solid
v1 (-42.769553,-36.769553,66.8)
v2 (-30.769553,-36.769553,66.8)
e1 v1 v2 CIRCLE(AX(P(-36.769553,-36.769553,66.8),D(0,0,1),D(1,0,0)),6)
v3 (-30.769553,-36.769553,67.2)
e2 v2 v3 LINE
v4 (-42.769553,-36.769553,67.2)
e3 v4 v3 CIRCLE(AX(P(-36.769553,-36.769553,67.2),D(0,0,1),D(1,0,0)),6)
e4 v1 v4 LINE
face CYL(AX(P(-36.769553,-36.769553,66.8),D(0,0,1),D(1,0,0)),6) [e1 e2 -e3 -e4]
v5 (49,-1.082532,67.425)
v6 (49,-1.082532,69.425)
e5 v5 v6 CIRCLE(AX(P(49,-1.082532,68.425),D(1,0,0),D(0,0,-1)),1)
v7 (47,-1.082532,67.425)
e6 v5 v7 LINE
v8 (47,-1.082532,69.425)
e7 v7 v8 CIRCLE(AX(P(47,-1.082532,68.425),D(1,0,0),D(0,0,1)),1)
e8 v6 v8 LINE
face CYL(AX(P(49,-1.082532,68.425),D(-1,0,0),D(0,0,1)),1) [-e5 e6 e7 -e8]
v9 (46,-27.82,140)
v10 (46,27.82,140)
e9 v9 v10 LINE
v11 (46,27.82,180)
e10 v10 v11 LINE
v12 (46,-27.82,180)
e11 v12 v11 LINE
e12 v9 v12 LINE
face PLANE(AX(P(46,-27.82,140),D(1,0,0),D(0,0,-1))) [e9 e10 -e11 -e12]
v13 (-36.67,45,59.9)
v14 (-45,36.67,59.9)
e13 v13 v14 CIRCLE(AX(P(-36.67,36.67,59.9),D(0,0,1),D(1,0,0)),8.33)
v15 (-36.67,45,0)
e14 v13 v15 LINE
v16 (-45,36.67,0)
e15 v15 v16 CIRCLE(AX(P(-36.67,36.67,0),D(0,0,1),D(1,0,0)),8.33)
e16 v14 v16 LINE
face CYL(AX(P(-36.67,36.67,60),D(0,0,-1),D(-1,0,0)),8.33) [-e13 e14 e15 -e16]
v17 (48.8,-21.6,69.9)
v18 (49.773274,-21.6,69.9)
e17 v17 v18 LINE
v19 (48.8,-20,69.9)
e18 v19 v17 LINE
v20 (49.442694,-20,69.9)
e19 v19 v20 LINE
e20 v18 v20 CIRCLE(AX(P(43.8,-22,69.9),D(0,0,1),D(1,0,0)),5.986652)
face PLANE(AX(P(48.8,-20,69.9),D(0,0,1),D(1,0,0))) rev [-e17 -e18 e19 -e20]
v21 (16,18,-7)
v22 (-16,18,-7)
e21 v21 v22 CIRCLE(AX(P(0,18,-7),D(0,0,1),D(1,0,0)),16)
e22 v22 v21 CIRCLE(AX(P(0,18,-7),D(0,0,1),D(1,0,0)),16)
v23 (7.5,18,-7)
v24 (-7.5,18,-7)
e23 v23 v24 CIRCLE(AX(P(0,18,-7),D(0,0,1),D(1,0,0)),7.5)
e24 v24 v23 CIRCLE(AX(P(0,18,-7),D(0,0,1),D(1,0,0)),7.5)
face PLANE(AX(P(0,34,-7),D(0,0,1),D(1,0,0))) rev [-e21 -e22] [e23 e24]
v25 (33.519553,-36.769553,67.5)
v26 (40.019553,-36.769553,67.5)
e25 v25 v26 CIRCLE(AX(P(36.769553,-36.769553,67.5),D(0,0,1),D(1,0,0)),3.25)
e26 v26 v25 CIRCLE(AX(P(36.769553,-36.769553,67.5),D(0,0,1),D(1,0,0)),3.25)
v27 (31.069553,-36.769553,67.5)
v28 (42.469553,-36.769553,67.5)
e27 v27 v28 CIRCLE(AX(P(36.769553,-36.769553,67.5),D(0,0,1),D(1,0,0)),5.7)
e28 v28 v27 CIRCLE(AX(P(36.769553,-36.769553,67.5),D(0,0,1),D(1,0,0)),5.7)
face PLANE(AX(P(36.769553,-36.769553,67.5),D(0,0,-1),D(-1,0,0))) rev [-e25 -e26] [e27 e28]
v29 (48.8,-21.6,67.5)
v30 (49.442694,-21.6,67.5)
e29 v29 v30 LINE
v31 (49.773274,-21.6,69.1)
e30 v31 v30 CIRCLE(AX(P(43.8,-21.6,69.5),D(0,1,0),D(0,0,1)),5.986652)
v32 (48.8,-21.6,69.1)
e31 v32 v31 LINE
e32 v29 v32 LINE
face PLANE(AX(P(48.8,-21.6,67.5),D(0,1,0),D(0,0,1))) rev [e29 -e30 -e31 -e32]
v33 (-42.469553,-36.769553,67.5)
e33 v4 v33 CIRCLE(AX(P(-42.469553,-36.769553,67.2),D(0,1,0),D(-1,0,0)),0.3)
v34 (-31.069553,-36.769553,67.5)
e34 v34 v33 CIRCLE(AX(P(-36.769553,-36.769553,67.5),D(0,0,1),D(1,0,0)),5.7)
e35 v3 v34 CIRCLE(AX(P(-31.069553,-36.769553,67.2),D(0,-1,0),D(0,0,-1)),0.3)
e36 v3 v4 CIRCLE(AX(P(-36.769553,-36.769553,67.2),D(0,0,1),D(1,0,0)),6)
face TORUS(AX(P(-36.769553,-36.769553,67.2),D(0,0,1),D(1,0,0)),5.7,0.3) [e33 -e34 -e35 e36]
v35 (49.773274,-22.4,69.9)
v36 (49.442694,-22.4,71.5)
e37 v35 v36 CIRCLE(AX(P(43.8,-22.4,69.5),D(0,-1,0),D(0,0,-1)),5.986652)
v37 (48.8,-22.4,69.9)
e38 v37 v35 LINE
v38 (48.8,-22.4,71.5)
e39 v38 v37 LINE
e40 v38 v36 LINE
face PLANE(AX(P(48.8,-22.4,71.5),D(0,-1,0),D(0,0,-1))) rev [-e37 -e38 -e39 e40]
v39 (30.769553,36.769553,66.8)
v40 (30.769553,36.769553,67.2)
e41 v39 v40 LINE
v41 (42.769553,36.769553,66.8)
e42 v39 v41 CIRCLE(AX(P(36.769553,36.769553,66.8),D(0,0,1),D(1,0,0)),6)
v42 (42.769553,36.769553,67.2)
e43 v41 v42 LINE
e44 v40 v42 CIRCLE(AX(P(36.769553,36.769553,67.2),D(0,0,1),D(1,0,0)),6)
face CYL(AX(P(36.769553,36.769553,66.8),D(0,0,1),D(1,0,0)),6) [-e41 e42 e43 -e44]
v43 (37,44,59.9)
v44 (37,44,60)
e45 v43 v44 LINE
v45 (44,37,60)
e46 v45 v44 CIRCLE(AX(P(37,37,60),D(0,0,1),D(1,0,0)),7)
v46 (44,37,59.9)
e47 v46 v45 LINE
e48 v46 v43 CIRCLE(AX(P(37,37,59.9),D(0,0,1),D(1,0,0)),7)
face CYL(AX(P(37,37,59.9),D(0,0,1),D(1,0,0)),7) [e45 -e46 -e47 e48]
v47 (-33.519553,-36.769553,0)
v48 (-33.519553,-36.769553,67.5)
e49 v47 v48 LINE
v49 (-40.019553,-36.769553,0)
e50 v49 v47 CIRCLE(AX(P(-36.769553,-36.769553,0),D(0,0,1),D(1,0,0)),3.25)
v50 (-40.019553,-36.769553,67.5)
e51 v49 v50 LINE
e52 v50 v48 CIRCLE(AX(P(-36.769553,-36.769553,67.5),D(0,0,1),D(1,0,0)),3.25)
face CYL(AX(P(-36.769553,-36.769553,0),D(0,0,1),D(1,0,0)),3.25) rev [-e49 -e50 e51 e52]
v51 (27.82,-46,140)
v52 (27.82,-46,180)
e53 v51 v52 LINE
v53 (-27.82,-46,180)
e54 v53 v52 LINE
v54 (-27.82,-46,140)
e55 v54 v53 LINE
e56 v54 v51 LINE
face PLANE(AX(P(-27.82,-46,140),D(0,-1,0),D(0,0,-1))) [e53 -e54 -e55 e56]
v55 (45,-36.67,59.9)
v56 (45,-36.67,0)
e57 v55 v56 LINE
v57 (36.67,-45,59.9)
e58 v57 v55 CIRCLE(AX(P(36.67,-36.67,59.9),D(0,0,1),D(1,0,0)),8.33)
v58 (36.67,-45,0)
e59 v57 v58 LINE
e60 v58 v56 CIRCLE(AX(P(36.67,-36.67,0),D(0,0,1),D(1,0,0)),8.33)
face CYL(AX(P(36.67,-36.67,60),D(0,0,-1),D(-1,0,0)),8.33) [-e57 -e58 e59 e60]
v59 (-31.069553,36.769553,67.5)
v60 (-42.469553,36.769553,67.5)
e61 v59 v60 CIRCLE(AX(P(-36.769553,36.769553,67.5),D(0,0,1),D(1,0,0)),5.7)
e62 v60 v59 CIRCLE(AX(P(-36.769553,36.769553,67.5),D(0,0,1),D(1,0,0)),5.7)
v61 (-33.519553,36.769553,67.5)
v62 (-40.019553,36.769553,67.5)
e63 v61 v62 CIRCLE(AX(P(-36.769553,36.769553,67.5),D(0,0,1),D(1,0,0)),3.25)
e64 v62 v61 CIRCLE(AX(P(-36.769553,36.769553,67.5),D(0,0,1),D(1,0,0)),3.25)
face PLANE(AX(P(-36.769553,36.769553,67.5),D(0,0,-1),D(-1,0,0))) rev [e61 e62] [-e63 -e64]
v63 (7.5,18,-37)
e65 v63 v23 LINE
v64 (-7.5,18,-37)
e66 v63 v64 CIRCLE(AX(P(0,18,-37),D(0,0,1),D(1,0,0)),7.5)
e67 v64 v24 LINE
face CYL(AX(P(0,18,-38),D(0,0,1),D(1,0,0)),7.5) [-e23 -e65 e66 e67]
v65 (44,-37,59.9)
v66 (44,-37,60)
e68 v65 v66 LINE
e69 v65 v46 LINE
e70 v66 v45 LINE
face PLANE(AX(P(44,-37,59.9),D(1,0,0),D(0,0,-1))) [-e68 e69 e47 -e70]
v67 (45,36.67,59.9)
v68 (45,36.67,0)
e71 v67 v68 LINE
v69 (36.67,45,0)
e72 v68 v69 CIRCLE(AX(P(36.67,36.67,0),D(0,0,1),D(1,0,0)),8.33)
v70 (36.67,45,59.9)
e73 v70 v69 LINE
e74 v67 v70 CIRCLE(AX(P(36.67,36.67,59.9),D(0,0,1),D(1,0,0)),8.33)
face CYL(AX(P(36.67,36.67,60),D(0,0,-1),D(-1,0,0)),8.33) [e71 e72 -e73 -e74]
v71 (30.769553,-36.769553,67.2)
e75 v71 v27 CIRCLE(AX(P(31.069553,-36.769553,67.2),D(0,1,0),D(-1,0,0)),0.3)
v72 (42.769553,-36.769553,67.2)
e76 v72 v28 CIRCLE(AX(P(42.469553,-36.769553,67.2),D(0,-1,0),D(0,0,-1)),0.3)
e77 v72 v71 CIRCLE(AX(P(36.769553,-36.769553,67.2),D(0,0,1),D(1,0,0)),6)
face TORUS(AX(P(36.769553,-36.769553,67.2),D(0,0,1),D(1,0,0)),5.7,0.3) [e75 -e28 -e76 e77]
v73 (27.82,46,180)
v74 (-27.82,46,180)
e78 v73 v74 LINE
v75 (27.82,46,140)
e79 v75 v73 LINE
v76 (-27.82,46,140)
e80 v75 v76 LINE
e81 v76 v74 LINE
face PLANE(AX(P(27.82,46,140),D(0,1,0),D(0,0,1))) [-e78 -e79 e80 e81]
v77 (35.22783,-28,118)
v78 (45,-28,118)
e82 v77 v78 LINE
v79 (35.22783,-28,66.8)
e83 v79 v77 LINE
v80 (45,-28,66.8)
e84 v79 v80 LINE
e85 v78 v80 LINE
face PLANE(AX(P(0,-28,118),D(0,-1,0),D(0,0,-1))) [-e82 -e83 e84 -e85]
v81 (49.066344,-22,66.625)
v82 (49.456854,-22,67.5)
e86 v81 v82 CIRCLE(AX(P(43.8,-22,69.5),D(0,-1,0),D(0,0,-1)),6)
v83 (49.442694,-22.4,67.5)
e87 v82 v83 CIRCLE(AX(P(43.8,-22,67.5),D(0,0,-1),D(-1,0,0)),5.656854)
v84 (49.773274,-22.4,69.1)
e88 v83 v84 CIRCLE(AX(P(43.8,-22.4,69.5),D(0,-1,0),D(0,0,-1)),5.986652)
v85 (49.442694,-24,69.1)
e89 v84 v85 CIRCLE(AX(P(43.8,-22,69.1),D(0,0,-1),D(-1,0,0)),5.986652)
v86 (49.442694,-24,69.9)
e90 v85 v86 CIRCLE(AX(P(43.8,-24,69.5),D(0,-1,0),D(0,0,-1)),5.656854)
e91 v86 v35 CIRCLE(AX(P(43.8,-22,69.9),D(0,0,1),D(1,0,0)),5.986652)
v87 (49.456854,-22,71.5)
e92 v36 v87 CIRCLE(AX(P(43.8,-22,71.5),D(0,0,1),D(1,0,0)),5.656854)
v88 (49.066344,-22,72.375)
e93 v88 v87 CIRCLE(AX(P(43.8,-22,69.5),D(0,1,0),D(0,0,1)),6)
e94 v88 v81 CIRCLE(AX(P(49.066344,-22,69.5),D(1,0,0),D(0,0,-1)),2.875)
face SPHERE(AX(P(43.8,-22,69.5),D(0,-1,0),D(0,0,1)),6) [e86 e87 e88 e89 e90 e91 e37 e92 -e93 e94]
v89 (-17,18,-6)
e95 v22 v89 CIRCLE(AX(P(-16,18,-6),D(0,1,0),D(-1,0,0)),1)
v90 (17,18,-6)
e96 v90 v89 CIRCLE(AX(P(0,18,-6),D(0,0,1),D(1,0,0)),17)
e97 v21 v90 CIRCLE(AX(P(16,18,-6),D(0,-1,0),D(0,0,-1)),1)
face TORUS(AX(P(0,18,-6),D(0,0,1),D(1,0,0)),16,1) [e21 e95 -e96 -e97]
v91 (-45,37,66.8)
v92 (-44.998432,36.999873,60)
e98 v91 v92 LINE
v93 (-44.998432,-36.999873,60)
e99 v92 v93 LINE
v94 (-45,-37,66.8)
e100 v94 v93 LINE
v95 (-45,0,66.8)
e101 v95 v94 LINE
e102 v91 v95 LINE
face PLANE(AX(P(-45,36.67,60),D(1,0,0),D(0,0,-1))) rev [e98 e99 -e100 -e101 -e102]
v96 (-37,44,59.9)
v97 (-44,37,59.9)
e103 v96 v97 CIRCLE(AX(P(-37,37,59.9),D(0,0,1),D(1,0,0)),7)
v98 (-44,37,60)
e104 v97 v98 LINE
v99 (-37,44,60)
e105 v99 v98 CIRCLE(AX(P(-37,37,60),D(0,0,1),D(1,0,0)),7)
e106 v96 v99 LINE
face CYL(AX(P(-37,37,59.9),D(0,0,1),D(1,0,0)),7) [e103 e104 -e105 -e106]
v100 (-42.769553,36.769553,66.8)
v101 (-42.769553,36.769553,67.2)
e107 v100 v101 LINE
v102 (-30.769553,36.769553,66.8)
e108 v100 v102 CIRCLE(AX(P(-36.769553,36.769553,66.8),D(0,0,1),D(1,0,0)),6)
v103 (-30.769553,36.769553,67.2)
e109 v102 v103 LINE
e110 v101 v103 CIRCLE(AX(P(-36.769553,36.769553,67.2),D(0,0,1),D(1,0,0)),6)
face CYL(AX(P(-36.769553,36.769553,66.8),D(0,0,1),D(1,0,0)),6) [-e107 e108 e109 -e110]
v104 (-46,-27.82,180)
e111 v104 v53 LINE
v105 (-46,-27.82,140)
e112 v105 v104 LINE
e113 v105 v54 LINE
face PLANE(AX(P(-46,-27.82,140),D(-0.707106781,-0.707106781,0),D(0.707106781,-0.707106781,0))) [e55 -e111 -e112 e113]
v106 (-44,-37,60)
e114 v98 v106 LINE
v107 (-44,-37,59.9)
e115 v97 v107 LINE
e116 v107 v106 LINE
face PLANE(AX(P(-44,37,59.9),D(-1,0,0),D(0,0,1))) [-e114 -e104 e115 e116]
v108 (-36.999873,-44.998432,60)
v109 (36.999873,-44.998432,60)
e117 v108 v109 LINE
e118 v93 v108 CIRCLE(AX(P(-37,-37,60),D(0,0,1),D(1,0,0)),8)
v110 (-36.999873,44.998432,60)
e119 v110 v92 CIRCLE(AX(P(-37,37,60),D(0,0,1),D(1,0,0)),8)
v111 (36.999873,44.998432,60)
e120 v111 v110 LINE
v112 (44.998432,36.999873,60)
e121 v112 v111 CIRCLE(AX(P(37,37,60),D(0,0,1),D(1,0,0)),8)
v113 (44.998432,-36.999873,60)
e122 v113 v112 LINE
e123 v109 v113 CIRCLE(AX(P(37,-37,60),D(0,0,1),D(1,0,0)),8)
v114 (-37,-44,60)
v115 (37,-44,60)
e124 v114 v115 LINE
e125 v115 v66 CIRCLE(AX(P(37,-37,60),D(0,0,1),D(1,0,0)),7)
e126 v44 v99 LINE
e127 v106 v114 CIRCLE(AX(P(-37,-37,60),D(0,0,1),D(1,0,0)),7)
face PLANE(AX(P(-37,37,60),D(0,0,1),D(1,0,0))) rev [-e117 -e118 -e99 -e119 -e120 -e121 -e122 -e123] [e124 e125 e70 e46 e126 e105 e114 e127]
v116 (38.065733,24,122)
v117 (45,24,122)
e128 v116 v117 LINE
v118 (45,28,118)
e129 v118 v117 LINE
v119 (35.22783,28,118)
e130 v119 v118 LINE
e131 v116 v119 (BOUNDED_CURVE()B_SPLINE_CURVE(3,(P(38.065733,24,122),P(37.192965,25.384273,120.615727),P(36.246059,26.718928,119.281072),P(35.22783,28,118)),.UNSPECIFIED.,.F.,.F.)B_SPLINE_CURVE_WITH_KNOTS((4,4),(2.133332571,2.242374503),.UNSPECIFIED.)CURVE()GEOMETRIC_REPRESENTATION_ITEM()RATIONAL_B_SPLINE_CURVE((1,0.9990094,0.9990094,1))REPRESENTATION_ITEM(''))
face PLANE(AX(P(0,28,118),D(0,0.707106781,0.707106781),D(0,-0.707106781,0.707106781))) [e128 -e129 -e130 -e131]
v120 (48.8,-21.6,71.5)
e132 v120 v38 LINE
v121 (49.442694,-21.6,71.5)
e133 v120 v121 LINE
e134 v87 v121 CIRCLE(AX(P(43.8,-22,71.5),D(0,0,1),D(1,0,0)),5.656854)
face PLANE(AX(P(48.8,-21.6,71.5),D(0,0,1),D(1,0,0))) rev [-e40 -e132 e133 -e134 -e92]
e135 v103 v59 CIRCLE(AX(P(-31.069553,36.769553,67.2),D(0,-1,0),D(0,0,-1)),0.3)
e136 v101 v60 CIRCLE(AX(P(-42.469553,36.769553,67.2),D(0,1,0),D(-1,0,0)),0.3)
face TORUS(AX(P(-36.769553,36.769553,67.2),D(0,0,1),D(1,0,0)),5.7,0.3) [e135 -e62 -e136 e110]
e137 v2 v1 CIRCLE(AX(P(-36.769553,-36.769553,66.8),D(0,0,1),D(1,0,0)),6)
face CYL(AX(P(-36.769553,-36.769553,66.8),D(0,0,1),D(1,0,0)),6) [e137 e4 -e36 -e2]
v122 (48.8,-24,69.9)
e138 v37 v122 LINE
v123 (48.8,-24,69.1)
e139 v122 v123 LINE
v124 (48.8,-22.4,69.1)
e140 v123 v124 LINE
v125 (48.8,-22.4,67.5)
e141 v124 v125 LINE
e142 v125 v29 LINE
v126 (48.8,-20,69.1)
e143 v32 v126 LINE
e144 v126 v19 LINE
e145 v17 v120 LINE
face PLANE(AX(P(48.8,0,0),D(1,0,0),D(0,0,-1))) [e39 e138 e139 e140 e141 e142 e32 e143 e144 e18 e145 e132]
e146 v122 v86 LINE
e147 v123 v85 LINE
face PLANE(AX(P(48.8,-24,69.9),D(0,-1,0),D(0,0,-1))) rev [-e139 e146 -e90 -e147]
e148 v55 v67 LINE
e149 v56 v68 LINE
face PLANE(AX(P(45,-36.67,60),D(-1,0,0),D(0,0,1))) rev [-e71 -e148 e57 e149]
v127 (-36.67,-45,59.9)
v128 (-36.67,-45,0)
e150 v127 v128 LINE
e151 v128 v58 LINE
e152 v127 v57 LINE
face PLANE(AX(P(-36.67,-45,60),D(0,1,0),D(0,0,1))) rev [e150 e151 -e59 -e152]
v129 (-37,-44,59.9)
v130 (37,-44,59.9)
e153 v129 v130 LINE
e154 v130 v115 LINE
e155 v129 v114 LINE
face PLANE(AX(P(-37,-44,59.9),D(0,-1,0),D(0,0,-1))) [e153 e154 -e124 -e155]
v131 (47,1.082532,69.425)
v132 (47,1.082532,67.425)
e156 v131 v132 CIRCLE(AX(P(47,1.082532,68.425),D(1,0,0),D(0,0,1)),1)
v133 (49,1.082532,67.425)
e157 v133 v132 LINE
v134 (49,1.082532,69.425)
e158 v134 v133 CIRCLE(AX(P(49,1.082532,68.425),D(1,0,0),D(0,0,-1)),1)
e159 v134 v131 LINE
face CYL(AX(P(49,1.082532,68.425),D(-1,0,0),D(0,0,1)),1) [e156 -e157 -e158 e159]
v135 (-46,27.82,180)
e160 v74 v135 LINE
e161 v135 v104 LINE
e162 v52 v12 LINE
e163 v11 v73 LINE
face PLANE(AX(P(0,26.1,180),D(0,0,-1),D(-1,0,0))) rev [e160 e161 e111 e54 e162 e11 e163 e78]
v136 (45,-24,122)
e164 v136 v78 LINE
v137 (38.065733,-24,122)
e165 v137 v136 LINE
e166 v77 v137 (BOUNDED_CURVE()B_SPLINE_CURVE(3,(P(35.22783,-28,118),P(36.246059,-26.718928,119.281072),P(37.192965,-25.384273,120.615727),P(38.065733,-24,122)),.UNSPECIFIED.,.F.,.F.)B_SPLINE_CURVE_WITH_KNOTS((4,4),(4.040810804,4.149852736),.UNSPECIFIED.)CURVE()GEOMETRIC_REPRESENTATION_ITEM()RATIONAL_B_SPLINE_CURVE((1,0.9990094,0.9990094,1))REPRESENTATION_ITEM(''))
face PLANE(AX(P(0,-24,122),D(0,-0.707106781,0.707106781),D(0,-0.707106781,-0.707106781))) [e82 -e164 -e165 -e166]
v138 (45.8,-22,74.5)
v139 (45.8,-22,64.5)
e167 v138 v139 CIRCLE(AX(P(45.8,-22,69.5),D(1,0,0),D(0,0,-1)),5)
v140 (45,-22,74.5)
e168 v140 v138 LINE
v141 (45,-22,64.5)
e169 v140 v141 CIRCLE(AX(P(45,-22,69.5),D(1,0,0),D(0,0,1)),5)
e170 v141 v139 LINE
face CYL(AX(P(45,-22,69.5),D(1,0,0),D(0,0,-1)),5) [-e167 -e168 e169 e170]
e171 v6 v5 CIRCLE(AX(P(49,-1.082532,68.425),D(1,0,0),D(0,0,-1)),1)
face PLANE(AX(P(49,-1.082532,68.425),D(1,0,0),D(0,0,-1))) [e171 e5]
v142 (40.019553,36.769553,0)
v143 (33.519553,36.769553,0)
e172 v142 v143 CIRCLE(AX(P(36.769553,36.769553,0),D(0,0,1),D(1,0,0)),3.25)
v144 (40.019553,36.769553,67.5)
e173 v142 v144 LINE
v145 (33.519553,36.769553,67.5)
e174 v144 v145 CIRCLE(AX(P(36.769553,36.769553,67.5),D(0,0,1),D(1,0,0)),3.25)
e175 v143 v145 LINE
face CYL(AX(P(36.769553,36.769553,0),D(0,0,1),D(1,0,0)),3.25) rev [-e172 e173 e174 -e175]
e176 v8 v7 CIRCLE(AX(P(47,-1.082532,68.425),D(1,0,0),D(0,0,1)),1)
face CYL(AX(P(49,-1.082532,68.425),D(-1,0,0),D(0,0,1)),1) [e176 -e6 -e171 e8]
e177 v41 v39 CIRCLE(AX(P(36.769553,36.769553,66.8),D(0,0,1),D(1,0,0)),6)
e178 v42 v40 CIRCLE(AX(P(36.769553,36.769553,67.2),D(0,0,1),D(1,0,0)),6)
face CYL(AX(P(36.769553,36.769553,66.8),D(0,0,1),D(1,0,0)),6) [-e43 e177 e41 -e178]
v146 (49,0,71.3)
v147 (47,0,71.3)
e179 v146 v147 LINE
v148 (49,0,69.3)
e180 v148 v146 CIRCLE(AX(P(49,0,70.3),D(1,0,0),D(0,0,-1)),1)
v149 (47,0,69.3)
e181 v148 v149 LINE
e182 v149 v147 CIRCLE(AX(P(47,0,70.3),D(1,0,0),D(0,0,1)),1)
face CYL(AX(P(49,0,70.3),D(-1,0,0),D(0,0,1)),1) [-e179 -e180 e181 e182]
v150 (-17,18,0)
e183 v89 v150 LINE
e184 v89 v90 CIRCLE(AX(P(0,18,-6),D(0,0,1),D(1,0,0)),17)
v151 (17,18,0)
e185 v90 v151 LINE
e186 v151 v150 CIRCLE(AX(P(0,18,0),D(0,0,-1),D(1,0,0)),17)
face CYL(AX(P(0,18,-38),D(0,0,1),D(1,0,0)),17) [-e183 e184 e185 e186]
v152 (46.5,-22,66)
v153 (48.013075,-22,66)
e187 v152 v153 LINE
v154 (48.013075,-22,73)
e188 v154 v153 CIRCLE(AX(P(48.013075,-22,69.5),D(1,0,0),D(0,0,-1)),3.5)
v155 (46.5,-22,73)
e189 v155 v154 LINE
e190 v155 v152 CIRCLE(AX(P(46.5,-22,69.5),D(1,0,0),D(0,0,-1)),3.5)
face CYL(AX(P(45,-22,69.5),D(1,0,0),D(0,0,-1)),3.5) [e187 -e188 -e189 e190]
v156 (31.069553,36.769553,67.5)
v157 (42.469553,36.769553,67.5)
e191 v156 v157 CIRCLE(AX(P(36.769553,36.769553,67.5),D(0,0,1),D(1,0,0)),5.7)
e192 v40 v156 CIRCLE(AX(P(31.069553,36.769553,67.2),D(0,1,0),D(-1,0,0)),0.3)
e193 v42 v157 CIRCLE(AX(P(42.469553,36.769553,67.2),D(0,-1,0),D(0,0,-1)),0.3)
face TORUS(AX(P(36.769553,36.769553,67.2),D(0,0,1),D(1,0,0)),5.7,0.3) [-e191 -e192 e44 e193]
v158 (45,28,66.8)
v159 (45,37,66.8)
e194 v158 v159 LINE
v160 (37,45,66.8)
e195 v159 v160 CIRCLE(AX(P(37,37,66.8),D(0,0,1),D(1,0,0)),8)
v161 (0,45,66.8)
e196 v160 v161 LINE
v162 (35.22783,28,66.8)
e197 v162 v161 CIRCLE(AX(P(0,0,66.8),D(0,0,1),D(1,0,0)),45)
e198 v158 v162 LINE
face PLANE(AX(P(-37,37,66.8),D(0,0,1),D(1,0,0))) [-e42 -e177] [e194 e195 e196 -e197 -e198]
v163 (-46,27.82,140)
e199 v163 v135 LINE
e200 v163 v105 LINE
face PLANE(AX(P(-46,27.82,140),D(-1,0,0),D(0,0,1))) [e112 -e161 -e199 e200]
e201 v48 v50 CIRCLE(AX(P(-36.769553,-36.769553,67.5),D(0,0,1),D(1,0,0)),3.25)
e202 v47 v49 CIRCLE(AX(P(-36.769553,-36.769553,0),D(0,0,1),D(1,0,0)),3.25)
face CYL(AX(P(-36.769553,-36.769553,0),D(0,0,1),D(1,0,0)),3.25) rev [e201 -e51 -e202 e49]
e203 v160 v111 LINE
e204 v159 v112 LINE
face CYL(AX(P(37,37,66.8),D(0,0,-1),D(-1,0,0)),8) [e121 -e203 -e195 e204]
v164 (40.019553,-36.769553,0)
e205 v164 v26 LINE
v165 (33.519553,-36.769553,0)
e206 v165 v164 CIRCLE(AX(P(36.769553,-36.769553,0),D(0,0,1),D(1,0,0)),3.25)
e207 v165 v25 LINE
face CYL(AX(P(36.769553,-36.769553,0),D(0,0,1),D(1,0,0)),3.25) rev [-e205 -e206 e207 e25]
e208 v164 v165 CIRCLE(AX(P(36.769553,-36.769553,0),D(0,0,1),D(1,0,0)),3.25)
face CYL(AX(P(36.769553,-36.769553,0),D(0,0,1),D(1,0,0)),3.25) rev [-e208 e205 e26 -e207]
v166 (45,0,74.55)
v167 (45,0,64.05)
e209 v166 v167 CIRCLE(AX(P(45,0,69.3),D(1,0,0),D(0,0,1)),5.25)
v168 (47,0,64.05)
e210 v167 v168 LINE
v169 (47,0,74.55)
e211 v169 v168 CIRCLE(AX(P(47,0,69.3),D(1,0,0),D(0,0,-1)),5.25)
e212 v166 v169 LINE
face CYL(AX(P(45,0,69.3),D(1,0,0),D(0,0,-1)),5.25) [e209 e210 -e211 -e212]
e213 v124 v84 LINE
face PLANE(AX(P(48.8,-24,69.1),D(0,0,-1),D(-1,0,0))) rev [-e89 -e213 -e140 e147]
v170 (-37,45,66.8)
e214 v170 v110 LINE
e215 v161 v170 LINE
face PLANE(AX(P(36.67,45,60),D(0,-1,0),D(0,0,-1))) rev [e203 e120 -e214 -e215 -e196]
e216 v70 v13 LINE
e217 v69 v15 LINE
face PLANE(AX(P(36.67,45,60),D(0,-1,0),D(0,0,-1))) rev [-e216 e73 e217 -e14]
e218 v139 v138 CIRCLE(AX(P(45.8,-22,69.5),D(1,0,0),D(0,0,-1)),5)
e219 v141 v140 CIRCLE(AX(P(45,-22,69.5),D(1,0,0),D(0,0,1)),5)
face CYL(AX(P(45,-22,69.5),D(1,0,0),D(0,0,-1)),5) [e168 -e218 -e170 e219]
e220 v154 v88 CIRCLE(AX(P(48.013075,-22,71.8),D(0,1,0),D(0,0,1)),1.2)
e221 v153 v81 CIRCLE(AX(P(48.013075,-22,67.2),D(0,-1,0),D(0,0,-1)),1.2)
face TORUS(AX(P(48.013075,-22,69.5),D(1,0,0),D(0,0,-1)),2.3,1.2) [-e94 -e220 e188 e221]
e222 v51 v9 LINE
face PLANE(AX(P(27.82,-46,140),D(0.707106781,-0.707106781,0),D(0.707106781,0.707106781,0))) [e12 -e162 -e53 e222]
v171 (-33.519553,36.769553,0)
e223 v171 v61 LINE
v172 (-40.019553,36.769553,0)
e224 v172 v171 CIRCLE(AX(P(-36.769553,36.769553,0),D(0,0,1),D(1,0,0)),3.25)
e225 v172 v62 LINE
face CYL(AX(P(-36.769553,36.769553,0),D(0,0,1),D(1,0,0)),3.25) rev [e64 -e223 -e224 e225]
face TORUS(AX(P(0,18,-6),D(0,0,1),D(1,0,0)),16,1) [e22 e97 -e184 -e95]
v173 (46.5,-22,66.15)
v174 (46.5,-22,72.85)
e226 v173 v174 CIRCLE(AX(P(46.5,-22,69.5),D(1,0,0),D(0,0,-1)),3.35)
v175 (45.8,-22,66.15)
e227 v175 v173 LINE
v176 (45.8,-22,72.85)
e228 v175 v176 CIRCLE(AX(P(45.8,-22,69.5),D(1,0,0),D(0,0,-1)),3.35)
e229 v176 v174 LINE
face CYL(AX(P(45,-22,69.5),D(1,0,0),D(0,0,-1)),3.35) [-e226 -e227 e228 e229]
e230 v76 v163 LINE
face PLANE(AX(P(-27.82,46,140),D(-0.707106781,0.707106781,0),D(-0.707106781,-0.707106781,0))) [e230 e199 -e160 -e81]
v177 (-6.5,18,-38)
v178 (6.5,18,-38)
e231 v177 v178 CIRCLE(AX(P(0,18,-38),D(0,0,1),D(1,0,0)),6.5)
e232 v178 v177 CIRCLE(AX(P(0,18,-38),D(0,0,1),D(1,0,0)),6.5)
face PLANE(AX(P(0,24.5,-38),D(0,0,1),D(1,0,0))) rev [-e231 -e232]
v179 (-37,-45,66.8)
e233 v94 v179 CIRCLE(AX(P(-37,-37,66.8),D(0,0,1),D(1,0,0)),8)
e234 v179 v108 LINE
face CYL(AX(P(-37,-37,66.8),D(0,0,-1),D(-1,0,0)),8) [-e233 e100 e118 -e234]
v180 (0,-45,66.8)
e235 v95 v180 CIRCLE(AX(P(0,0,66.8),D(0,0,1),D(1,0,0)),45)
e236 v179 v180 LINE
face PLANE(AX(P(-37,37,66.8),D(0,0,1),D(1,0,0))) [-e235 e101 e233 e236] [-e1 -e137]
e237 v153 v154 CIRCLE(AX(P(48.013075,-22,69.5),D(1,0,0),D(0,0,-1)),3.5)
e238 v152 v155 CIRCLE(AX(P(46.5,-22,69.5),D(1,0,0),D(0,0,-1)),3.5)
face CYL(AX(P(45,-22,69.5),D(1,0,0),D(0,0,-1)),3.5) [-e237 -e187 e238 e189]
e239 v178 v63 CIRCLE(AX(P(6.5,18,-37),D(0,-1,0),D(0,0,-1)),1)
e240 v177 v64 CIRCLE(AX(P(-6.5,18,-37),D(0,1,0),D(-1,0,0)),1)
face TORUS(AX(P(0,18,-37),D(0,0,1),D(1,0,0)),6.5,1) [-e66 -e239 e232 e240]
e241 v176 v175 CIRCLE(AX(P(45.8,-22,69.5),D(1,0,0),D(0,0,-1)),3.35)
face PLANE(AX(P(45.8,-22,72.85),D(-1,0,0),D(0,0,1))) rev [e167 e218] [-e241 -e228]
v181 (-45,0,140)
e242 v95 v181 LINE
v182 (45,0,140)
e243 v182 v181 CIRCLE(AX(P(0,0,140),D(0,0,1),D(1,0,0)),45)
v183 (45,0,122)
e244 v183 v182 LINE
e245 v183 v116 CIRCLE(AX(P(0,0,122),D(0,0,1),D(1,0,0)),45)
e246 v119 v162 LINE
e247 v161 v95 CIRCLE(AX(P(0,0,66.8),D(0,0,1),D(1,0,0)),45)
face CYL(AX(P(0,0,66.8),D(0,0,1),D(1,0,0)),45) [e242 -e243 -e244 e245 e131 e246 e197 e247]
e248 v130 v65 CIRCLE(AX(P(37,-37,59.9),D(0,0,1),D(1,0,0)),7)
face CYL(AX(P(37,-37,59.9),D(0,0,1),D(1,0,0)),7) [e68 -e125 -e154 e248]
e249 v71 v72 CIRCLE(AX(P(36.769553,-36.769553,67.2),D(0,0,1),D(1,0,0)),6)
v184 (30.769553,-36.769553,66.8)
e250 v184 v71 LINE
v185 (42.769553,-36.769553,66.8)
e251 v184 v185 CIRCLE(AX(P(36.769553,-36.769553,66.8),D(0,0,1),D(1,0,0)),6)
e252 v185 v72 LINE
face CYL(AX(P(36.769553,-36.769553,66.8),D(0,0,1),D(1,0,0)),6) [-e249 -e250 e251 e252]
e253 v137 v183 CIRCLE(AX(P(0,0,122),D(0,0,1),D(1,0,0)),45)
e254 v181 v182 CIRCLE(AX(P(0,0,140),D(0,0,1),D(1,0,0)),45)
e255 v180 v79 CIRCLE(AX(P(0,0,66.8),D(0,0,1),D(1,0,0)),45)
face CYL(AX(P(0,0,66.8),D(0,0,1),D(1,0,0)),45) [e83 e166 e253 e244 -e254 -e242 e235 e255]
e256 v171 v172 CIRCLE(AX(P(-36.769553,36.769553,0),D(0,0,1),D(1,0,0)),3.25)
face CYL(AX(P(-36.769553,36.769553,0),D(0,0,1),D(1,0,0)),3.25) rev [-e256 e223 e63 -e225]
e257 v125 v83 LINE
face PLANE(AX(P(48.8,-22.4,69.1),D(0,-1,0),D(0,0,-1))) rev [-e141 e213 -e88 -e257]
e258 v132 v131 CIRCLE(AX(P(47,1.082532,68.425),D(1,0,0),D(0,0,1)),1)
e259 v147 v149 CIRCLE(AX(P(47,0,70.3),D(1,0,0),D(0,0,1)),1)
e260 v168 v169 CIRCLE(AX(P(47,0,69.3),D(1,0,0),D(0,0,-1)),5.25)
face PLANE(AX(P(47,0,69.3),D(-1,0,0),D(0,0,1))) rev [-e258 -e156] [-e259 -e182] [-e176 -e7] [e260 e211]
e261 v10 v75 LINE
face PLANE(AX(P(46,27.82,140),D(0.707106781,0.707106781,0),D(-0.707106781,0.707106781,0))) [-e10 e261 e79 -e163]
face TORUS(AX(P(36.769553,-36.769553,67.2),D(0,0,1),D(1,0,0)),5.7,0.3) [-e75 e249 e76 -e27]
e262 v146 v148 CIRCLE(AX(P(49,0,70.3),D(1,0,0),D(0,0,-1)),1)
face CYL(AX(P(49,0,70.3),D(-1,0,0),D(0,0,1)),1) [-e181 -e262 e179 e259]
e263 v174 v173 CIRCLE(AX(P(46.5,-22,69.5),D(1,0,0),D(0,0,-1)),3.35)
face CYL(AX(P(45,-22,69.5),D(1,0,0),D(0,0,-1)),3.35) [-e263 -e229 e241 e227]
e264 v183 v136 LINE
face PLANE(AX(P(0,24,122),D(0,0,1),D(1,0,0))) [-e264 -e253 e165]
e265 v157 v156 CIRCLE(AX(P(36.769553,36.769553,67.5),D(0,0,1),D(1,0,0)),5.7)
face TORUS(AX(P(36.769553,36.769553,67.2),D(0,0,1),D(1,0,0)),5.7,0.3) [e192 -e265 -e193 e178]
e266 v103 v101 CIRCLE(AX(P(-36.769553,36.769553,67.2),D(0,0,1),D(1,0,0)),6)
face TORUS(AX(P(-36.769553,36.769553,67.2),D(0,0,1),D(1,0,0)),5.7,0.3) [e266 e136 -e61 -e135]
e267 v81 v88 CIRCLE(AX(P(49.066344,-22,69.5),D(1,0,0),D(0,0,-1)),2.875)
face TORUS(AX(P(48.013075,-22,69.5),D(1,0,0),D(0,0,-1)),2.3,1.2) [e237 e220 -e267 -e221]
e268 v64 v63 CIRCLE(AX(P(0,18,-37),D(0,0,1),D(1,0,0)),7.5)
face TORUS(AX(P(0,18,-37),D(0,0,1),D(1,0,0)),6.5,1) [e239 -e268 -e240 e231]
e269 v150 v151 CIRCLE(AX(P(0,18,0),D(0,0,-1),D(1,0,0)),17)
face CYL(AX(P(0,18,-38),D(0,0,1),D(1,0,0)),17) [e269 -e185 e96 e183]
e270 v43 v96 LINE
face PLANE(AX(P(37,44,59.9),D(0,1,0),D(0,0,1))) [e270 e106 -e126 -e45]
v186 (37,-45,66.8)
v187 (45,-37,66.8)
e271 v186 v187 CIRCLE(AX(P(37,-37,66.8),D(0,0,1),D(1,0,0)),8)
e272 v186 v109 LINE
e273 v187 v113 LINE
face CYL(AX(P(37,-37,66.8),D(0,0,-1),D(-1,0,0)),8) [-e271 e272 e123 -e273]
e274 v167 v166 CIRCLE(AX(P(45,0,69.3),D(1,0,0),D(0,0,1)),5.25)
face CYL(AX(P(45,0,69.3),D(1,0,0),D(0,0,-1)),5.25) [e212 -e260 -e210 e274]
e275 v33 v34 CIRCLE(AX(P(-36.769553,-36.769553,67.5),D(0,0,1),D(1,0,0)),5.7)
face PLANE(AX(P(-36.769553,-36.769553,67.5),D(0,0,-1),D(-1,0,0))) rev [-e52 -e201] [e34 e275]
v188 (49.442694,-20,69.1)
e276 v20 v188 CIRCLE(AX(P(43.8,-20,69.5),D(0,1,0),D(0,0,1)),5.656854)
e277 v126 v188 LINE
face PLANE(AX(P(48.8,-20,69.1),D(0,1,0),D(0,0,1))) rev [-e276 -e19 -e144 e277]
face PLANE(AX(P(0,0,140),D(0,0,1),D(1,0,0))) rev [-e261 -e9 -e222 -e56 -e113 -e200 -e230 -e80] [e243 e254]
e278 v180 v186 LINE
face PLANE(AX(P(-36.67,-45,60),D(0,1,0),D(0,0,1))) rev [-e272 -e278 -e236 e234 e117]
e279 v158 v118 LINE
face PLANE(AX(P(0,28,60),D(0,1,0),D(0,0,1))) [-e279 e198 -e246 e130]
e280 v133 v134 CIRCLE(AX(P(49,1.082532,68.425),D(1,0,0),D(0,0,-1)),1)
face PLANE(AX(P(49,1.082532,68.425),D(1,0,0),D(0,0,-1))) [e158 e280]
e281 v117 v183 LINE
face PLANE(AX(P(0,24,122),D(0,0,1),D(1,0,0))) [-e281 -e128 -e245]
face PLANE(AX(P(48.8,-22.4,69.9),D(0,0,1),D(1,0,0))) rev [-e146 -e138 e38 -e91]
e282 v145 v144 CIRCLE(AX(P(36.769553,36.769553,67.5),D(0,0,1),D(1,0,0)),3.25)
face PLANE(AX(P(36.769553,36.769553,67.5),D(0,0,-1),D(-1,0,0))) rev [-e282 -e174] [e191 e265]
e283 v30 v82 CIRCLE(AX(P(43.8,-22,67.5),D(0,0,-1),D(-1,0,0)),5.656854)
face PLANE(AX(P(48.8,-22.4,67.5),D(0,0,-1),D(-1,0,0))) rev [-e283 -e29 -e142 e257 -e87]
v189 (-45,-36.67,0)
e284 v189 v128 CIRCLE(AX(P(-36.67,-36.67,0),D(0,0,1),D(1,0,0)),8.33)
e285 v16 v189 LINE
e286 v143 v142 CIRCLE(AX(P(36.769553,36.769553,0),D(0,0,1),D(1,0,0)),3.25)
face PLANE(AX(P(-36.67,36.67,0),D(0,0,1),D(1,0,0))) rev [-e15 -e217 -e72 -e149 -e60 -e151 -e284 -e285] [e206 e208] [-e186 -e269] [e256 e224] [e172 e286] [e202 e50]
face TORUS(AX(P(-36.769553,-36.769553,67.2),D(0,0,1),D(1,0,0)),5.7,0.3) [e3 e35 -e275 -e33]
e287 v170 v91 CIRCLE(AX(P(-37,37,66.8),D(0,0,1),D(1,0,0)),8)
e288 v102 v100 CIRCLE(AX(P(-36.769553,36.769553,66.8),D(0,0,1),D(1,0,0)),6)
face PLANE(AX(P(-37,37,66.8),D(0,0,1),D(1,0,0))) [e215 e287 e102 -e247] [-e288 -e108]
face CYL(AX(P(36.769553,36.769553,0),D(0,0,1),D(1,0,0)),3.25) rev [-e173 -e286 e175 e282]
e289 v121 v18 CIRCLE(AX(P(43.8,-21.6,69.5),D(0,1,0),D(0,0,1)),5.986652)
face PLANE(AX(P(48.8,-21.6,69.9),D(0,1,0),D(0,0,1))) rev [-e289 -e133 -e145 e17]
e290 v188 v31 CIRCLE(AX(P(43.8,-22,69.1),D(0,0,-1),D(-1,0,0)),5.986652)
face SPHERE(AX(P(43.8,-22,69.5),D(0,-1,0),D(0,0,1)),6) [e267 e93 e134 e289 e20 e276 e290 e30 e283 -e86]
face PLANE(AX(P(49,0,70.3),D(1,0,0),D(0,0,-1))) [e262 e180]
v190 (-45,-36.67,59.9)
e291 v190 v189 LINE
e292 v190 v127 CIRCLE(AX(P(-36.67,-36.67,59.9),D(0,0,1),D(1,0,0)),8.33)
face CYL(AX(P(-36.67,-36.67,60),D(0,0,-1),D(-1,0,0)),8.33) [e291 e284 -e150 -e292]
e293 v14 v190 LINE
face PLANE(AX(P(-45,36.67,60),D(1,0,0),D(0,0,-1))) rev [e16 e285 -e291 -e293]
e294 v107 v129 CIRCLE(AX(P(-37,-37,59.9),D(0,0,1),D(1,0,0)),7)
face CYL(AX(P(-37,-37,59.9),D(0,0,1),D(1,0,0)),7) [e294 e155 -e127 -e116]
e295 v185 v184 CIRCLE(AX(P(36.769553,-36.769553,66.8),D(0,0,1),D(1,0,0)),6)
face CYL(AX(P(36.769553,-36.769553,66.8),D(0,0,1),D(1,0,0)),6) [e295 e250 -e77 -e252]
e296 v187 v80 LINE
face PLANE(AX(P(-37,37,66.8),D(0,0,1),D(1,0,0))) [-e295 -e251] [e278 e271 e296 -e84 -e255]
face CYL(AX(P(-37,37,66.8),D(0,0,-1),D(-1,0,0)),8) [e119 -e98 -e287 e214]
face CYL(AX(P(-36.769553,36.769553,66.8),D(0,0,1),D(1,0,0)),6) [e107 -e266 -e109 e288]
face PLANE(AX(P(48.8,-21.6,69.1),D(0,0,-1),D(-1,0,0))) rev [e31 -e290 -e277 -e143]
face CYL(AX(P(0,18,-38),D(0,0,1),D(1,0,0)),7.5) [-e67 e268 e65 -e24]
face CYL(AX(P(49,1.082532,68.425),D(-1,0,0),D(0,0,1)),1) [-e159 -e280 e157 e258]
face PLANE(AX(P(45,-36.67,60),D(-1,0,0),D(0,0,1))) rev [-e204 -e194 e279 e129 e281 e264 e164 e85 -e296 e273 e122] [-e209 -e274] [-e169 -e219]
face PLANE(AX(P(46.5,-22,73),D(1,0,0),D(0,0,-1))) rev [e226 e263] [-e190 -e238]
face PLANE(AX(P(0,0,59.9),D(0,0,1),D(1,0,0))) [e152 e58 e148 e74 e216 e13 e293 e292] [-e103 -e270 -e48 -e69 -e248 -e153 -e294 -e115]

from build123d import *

# Parameters (mm, degrees)
EXTRUDE_1_DEPTH             = 60
EXTRUDE_2_DEPTH             = 6.8
SKETCH_4_W                  = 90
SKETCH_4_H                  = 90
CUT_EXTRUDE_1_DEPTH         = 0.1
EXTRUDE_3_DEPTH             = 45
PATTERN_LINEAR_1_COUNT      = 2
PATTERN_LINEAR_1_PITCH      = 73.539105243
PATTERN_LINEAR_1_COUNT_DIR2 = 2
PATTERN_LINEAR_1_PITCH_DIR2 = 73.539105243
SKETCH_9_W                  = 2
SKETCH_9_H                  = 5.25
SKETCH_10_R                 = 1
EXTRUDE_4_DEPTH             = 2
SKETCH_11_R                 = 1
EXTRUDE_5_DEPTH             = 2
SKETCH_12_R                 = 1
EXTRUDE_6_DEPTH             = 2
CUT_EXTRUDE_2_DEPTH         = 1
EXTRUDE_7_DEPTH             = 40
SKETCH_16_W                 = 67.5
SKETCH_16_H                 = 3.25
PATTERN_LINEAR_2_COUNT      = 2
PATTERN_LINEAR_2_PITCH      = 73.539105243
PATTERN_LINEAR_2_COUNT_DIR2 = 2
PATTERN_LINEAR_2_PITCH_DIR2 = 73.539105243


with BuildPart() as part:
    # 草图1 → 凸台-拉伸1 (new body)
    with BuildSketch(Plane.XY):
        with BuildLine():
            Line((-45, 36.67), (-45, -36.67))
            ThreePointArc((-45, -36.67), (-42.560199487, -42.560199487), (-36.67, -45))
            Line((-36.67, -45), (36.67, -45))
            ThreePointArc((36.67, -45), (42.560199487, -42.560199487), (45, -36.67))
            Line((45, -36.67), (45, 36.67))
            ThreePointArc((45, 36.67), (42.560199487, 42.560199487), (36.67, 45))
            Line((36.67, 45), (-36.67, 45))
            ThreePointArc((-36.67, 45), (-42.560199487, 42.560199487), (-45, 36.67))
        make_face()
    extrude(amount=EXTRUDE_1_DEPTH)

    # 草图2 → 旋转1 (revolve)
    with BuildSketch(Plane(origin=(0, 0, 0), x_dir=(0, 0, -1), z_dir=(1, 0, 0)), mode=Mode.PRIVATE) as revolve_1_sk:
        with BuildLine():
            Line((0, 18), (0, 35))
            Line((0, 35), (6, 35))
            ThreePointArc((6, 35), (6.707106781, 34.707106781), (7, 34))
            Line((7, 34), (7, 25.5))
            Line((7, 25.5), (37, 25.5))
            ThreePointArc((37, 25.5), (37.707106781, 25.207106781), (38, 24.5))
            Line((38, 24.5), (38, 18))
            Line((38, 18), (0, 18))
        make_face()
    revolve(revolve_1_sk.sketch.rotate(Axis((0, 18, -38), (0, 0, 1)), 270), axis=Axis((0, 18, -38), (0, 0, 1)))

    # 草图3 → 凸台-拉伸2 (add)
    with BuildSketch(Plane.XY.offset(60)):
        with BuildLine():
            Line((-45, 37), (-45, -37))
            ThreePointArc((-45, -37), (-42.656854249, -42.656854249), (-37, -45))
            Line((-37, -45), (37, -45))
            ThreePointArc((37, -45), (42.656854249, -42.656854249), (45, -37))
            Line((45, -37), (45, 37))
            ThreePointArc((45, 37), (42.656854249, 42.656854249), (37, 45))
            Line((37, 45), (-37, 45))
            ThreePointArc((-37, 45), (-42.656854249, 42.656854249), (-45, 37))
        make_face()
    extrude(amount=EXTRUDE_2_DEPTH)

    # 草图4 → 切除-拉伸1 (cut)
    with BuildSketch(Plane.XY.offset(60)):
        Rectangle(SKETCH_4_W, SKETCH_4_H)
        with BuildLine():
            Line((-44, 37), (-44, -37))
            ThreePointArc((-44, -37), (-41.949747468, -41.949747468), (-37, -44))
            Line((-37, -44), (37, -44))
            ThreePointArc((37, -44), (41.949747468, -41.949747468), (44, -37))
            Line((44, -37), (44, 37))
            ThreePointArc((44, 37), (41.949747468, 41.949747468), (37, 44))
            Line((37, 44), (-37, 44))
            ThreePointArc((-37, 44), (-41.949747468, 41.949747468), (-44, 37))
        make_face(mode=Mode.SUBTRACT)
    extrude(amount=-CUT_EXTRUDE_1_DEPTH, mode=Mode.SUBTRACT)

    # 草图5 → 旋转2 (revolve)
    with BuildSketch(Plane(origin=(0, 0, 0), x_dir=(0, 0, -1), z_dir=(1, 0, 0)), mode=Mode.PRIVATE) as revolve_2_sk:
        Polygon((-175.5, 0), (-175.5, 26.1), (-180, 26.1), (-180, 42.5), (-179, 43.5), (-175.5, 43.5), (-175.5, 45), (-66.8, 45), (-66.8, 0), align=None)
    revolve(revolve_2_sk.sketch.rotate(Axis((0, 0, 66.8), (0, 0, 1)), 270), axis=Axis((0, 0, 66.8), (0, 0, 1)))

    # 草图6 → 凸台-拉伸3 (add)
    with BuildSketch(Plane(origin=(45, 0, 0), x_dir=(0, 0, -1), z_dir=(1, 0, 0))):
        Polygon((-122, -24), (-118, -28), (-60, -28), (-60, 28), (-118, 28), (-122, 24), align=None)
    extrude(amount=-EXTRUDE_3_DEPTH)

    # 草图7 → 旋转3 (revolve)
    with BuildSketch(Plane(origin=(0, 0, 0), x_dir=(0, 0, -1), z_dir=(0.7071067811865476, 0.7071067811865475, 0)), mode=Mode.PRIVATE) as revolve_3_sk:
        with BuildLine():
            Line((-67.5, -52), (-67.5, -46.3))
            ThreePointArc((-67.5, -46.3), (-67.412132034, -46.087867966), (-67.2, -46))
            Line((-67.2, -46), (-66.8, -46))
            Line((-66.8, -46), (-66.8, -52))
            Line((-66.8, -52), (-67.5, -52))
        make_face()
    revolve_3 = revolve(revolve_3_sk.sketch.rotate(Axis((36.769552622, -36.769552622, 66.8), (0, 0, 1)), 225), axis=Axis((36.769552622, -36.769552622, 66.8), (0, 0, 1)))

    # 阵列(线性)1: Revolve 3 2 × 2
    with Locations(*[(-j * PATTERN_LINEAR_1_PITCH_DIR2, i * PATTERN_LINEAR_1_PITCH, 0) for i in range(PATTERN_LINEAR_1_COUNT) for j in range(PATTERN_LINEAR_1_COUNT_DIR2) if (i, j) != (0, 0)]):
        add(revolve_3)

    # 草图9 → 旋转4 (revolve)
    with BuildSketch(Plane(origin=(0, 0, 0), x_dir=(1, 0, 0), z_dir=(0, 1, 0)), mode=Mode.PRIVATE) as revolve_4_sk:
        with Locations((46, -71.925)):
            Rectangle(SKETCH_9_W, SKETCH_9_H)
    revolve(revolve_4_sk.sketch.rotate(Axis((45, 0, 69.3), (1, 0, 0)), 180), axis=Axis((45, 0, 69.3), (1, 0, 0)))

    # 草图10 → 凸台-拉伸4 (add)
    with BuildSketch(Plane(origin=(47, 0, 0), x_dir=(0, 0, -1), z_dir=(1, 0, 0))):
        with Locations(Location((-70.3, 0, 0), (0, 0, 180))):
            Circle(SKETCH_10_R)
    extrude(amount=EXTRUDE_4_DEPTH)

    # 草图11 → 凸台-拉伸5 (add)
    with BuildSketch(Plane(origin=(47, 0, 0), x_dir=(0, 0, -1), z_dir=(1, 0, 0))):
        with Locations(Location((-68.425, -1.082531755, 0), (0, 0, 180))):
            Circle(SKETCH_11_R)
    extrude(amount=EXTRUDE_5_DEPTH)

    # 草图12 → 凸台-拉伸6 (add)
    with BuildSketch(Plane(origin=(47, 0, 0), x_dir=(0, 0, -1), z_dir=(1, 0, 0))):
        with Locations(Location((-68.425, 1.082531755, 0), (0, 0, 180))):
            Circle(SKETCH_12_R)
    extrude(amount=EXTRUDE_6_DEPTH)

    # 草图13 → 旋转5 (revolve)
    with BuildSketch(Plane(origin=(0, -22, 0), x_dir=(1, 0, 0), z_dir=(0, 1, 0)), mode=Mode.PRIVATE) as revolve_5_sk:
        with BuildLine():
            Line((48.013074887, -73), (46.5, -73))
            Line((46.5, -73), (46.5, -72.85))
            Line((46.5, -72.85), (45.8, -72.85))
            Line((45.8, -72.85), (45.8, -74.5))
            Line((45.8, -74.5), (45, -74.5))
            Line((45, -74.5), (45, -69.5))
            Line((45, -69.5), (49.8, -69.5))
            ThreePointArc((49.8, -69.5), (49.613693389, -70.98356637), (49.066343608, -72.375))
            ThreePointArc((49.066343608, -72.375), (48.625447322, -72.831988372), (48.013074887, -73))
        make_face()
    revolve(revolve_5_sk.sketch.rotate(Axis((45, -22, 69.5), (1, 0, 0)), 180), axis=Axis((45, -22, 69.5), (1, 0, 0)))

    # 草图14 → 切除-拉伸2 (cut)
    with BuildSketch(Plane(origin=(49.8, 0, 0), x_dir=(0, 0, -1), z_dir=(1, 0, 0))):
        Polygon((-71.5, -21.6), (-71.5, -22.4), (-69.9, -22.4), (-69.9, -24), (-69.1, -24), (-69.1, -22.4), (-67.5, -22.4), (-67.5, -21.6), (-69.1, -21.6), (-69.1, -20), (-69.9, -20), (-69.9, -21.6), align=None)
    extrude(amount=-CUT_EXTRUDE_2_DEPTH, mode=Mode.SUBTRACT)

    # 草图15 → 凸台-拉伸7 (add)
    with BuildSketch(Plane.XY.offset(180)):
        Polygon((-46, -27.82), (-27.82, -46), (27.82, -46), (46, -27.82), (46, 27.82), (27.82, 46), (-27.82, 46), (-46, 27.82), align=None)
    extrude(amount=-EXTRUDE_7_DEPTH)

    # 草图16 → 切除-旋转1 (revolve, cut)
    with BuildSketch(Plane(origin=(0, 0, 0), x_dir=(0, 0, -1), z_dir=(0.7071067811865476, 0.7071067811865475, 0)), mode=Mode.PRIVATE) as cut_revolve_1_sk:
        with Locations((-33.75, -50.375)):
            Rectangle(SKETCH_16_W, SKETCH_16_H)
    cut_revolve_1 = revolve(cut_revolve_1_sk.sketch.rotate(Axis((36.769552622, -36.769552622, 0), (0, 0, 1)), 225), axis=Axis((36.769552622, -36.769552622, 0), (0, 0, 1)), mode=Mode.SUBTRACT)

    # 阵列(线性)2: Cut-Revolve 1 2 × 2
    with Locations(*[(-j * PATTERN_LINEAR_2_PITCH_DIR2, i * PATTERN_LINEAR_2_PITCH, 0) for i in range(PATTERN_LINEAR_2_COUNT) for j in range(PATTERN_LINEAR_2_COUNT_DIR2) if (i, j) != (0, 0)]):
        add(cut_revolve_1, mode=Mode.SUBTRACT)


solid = part.part
